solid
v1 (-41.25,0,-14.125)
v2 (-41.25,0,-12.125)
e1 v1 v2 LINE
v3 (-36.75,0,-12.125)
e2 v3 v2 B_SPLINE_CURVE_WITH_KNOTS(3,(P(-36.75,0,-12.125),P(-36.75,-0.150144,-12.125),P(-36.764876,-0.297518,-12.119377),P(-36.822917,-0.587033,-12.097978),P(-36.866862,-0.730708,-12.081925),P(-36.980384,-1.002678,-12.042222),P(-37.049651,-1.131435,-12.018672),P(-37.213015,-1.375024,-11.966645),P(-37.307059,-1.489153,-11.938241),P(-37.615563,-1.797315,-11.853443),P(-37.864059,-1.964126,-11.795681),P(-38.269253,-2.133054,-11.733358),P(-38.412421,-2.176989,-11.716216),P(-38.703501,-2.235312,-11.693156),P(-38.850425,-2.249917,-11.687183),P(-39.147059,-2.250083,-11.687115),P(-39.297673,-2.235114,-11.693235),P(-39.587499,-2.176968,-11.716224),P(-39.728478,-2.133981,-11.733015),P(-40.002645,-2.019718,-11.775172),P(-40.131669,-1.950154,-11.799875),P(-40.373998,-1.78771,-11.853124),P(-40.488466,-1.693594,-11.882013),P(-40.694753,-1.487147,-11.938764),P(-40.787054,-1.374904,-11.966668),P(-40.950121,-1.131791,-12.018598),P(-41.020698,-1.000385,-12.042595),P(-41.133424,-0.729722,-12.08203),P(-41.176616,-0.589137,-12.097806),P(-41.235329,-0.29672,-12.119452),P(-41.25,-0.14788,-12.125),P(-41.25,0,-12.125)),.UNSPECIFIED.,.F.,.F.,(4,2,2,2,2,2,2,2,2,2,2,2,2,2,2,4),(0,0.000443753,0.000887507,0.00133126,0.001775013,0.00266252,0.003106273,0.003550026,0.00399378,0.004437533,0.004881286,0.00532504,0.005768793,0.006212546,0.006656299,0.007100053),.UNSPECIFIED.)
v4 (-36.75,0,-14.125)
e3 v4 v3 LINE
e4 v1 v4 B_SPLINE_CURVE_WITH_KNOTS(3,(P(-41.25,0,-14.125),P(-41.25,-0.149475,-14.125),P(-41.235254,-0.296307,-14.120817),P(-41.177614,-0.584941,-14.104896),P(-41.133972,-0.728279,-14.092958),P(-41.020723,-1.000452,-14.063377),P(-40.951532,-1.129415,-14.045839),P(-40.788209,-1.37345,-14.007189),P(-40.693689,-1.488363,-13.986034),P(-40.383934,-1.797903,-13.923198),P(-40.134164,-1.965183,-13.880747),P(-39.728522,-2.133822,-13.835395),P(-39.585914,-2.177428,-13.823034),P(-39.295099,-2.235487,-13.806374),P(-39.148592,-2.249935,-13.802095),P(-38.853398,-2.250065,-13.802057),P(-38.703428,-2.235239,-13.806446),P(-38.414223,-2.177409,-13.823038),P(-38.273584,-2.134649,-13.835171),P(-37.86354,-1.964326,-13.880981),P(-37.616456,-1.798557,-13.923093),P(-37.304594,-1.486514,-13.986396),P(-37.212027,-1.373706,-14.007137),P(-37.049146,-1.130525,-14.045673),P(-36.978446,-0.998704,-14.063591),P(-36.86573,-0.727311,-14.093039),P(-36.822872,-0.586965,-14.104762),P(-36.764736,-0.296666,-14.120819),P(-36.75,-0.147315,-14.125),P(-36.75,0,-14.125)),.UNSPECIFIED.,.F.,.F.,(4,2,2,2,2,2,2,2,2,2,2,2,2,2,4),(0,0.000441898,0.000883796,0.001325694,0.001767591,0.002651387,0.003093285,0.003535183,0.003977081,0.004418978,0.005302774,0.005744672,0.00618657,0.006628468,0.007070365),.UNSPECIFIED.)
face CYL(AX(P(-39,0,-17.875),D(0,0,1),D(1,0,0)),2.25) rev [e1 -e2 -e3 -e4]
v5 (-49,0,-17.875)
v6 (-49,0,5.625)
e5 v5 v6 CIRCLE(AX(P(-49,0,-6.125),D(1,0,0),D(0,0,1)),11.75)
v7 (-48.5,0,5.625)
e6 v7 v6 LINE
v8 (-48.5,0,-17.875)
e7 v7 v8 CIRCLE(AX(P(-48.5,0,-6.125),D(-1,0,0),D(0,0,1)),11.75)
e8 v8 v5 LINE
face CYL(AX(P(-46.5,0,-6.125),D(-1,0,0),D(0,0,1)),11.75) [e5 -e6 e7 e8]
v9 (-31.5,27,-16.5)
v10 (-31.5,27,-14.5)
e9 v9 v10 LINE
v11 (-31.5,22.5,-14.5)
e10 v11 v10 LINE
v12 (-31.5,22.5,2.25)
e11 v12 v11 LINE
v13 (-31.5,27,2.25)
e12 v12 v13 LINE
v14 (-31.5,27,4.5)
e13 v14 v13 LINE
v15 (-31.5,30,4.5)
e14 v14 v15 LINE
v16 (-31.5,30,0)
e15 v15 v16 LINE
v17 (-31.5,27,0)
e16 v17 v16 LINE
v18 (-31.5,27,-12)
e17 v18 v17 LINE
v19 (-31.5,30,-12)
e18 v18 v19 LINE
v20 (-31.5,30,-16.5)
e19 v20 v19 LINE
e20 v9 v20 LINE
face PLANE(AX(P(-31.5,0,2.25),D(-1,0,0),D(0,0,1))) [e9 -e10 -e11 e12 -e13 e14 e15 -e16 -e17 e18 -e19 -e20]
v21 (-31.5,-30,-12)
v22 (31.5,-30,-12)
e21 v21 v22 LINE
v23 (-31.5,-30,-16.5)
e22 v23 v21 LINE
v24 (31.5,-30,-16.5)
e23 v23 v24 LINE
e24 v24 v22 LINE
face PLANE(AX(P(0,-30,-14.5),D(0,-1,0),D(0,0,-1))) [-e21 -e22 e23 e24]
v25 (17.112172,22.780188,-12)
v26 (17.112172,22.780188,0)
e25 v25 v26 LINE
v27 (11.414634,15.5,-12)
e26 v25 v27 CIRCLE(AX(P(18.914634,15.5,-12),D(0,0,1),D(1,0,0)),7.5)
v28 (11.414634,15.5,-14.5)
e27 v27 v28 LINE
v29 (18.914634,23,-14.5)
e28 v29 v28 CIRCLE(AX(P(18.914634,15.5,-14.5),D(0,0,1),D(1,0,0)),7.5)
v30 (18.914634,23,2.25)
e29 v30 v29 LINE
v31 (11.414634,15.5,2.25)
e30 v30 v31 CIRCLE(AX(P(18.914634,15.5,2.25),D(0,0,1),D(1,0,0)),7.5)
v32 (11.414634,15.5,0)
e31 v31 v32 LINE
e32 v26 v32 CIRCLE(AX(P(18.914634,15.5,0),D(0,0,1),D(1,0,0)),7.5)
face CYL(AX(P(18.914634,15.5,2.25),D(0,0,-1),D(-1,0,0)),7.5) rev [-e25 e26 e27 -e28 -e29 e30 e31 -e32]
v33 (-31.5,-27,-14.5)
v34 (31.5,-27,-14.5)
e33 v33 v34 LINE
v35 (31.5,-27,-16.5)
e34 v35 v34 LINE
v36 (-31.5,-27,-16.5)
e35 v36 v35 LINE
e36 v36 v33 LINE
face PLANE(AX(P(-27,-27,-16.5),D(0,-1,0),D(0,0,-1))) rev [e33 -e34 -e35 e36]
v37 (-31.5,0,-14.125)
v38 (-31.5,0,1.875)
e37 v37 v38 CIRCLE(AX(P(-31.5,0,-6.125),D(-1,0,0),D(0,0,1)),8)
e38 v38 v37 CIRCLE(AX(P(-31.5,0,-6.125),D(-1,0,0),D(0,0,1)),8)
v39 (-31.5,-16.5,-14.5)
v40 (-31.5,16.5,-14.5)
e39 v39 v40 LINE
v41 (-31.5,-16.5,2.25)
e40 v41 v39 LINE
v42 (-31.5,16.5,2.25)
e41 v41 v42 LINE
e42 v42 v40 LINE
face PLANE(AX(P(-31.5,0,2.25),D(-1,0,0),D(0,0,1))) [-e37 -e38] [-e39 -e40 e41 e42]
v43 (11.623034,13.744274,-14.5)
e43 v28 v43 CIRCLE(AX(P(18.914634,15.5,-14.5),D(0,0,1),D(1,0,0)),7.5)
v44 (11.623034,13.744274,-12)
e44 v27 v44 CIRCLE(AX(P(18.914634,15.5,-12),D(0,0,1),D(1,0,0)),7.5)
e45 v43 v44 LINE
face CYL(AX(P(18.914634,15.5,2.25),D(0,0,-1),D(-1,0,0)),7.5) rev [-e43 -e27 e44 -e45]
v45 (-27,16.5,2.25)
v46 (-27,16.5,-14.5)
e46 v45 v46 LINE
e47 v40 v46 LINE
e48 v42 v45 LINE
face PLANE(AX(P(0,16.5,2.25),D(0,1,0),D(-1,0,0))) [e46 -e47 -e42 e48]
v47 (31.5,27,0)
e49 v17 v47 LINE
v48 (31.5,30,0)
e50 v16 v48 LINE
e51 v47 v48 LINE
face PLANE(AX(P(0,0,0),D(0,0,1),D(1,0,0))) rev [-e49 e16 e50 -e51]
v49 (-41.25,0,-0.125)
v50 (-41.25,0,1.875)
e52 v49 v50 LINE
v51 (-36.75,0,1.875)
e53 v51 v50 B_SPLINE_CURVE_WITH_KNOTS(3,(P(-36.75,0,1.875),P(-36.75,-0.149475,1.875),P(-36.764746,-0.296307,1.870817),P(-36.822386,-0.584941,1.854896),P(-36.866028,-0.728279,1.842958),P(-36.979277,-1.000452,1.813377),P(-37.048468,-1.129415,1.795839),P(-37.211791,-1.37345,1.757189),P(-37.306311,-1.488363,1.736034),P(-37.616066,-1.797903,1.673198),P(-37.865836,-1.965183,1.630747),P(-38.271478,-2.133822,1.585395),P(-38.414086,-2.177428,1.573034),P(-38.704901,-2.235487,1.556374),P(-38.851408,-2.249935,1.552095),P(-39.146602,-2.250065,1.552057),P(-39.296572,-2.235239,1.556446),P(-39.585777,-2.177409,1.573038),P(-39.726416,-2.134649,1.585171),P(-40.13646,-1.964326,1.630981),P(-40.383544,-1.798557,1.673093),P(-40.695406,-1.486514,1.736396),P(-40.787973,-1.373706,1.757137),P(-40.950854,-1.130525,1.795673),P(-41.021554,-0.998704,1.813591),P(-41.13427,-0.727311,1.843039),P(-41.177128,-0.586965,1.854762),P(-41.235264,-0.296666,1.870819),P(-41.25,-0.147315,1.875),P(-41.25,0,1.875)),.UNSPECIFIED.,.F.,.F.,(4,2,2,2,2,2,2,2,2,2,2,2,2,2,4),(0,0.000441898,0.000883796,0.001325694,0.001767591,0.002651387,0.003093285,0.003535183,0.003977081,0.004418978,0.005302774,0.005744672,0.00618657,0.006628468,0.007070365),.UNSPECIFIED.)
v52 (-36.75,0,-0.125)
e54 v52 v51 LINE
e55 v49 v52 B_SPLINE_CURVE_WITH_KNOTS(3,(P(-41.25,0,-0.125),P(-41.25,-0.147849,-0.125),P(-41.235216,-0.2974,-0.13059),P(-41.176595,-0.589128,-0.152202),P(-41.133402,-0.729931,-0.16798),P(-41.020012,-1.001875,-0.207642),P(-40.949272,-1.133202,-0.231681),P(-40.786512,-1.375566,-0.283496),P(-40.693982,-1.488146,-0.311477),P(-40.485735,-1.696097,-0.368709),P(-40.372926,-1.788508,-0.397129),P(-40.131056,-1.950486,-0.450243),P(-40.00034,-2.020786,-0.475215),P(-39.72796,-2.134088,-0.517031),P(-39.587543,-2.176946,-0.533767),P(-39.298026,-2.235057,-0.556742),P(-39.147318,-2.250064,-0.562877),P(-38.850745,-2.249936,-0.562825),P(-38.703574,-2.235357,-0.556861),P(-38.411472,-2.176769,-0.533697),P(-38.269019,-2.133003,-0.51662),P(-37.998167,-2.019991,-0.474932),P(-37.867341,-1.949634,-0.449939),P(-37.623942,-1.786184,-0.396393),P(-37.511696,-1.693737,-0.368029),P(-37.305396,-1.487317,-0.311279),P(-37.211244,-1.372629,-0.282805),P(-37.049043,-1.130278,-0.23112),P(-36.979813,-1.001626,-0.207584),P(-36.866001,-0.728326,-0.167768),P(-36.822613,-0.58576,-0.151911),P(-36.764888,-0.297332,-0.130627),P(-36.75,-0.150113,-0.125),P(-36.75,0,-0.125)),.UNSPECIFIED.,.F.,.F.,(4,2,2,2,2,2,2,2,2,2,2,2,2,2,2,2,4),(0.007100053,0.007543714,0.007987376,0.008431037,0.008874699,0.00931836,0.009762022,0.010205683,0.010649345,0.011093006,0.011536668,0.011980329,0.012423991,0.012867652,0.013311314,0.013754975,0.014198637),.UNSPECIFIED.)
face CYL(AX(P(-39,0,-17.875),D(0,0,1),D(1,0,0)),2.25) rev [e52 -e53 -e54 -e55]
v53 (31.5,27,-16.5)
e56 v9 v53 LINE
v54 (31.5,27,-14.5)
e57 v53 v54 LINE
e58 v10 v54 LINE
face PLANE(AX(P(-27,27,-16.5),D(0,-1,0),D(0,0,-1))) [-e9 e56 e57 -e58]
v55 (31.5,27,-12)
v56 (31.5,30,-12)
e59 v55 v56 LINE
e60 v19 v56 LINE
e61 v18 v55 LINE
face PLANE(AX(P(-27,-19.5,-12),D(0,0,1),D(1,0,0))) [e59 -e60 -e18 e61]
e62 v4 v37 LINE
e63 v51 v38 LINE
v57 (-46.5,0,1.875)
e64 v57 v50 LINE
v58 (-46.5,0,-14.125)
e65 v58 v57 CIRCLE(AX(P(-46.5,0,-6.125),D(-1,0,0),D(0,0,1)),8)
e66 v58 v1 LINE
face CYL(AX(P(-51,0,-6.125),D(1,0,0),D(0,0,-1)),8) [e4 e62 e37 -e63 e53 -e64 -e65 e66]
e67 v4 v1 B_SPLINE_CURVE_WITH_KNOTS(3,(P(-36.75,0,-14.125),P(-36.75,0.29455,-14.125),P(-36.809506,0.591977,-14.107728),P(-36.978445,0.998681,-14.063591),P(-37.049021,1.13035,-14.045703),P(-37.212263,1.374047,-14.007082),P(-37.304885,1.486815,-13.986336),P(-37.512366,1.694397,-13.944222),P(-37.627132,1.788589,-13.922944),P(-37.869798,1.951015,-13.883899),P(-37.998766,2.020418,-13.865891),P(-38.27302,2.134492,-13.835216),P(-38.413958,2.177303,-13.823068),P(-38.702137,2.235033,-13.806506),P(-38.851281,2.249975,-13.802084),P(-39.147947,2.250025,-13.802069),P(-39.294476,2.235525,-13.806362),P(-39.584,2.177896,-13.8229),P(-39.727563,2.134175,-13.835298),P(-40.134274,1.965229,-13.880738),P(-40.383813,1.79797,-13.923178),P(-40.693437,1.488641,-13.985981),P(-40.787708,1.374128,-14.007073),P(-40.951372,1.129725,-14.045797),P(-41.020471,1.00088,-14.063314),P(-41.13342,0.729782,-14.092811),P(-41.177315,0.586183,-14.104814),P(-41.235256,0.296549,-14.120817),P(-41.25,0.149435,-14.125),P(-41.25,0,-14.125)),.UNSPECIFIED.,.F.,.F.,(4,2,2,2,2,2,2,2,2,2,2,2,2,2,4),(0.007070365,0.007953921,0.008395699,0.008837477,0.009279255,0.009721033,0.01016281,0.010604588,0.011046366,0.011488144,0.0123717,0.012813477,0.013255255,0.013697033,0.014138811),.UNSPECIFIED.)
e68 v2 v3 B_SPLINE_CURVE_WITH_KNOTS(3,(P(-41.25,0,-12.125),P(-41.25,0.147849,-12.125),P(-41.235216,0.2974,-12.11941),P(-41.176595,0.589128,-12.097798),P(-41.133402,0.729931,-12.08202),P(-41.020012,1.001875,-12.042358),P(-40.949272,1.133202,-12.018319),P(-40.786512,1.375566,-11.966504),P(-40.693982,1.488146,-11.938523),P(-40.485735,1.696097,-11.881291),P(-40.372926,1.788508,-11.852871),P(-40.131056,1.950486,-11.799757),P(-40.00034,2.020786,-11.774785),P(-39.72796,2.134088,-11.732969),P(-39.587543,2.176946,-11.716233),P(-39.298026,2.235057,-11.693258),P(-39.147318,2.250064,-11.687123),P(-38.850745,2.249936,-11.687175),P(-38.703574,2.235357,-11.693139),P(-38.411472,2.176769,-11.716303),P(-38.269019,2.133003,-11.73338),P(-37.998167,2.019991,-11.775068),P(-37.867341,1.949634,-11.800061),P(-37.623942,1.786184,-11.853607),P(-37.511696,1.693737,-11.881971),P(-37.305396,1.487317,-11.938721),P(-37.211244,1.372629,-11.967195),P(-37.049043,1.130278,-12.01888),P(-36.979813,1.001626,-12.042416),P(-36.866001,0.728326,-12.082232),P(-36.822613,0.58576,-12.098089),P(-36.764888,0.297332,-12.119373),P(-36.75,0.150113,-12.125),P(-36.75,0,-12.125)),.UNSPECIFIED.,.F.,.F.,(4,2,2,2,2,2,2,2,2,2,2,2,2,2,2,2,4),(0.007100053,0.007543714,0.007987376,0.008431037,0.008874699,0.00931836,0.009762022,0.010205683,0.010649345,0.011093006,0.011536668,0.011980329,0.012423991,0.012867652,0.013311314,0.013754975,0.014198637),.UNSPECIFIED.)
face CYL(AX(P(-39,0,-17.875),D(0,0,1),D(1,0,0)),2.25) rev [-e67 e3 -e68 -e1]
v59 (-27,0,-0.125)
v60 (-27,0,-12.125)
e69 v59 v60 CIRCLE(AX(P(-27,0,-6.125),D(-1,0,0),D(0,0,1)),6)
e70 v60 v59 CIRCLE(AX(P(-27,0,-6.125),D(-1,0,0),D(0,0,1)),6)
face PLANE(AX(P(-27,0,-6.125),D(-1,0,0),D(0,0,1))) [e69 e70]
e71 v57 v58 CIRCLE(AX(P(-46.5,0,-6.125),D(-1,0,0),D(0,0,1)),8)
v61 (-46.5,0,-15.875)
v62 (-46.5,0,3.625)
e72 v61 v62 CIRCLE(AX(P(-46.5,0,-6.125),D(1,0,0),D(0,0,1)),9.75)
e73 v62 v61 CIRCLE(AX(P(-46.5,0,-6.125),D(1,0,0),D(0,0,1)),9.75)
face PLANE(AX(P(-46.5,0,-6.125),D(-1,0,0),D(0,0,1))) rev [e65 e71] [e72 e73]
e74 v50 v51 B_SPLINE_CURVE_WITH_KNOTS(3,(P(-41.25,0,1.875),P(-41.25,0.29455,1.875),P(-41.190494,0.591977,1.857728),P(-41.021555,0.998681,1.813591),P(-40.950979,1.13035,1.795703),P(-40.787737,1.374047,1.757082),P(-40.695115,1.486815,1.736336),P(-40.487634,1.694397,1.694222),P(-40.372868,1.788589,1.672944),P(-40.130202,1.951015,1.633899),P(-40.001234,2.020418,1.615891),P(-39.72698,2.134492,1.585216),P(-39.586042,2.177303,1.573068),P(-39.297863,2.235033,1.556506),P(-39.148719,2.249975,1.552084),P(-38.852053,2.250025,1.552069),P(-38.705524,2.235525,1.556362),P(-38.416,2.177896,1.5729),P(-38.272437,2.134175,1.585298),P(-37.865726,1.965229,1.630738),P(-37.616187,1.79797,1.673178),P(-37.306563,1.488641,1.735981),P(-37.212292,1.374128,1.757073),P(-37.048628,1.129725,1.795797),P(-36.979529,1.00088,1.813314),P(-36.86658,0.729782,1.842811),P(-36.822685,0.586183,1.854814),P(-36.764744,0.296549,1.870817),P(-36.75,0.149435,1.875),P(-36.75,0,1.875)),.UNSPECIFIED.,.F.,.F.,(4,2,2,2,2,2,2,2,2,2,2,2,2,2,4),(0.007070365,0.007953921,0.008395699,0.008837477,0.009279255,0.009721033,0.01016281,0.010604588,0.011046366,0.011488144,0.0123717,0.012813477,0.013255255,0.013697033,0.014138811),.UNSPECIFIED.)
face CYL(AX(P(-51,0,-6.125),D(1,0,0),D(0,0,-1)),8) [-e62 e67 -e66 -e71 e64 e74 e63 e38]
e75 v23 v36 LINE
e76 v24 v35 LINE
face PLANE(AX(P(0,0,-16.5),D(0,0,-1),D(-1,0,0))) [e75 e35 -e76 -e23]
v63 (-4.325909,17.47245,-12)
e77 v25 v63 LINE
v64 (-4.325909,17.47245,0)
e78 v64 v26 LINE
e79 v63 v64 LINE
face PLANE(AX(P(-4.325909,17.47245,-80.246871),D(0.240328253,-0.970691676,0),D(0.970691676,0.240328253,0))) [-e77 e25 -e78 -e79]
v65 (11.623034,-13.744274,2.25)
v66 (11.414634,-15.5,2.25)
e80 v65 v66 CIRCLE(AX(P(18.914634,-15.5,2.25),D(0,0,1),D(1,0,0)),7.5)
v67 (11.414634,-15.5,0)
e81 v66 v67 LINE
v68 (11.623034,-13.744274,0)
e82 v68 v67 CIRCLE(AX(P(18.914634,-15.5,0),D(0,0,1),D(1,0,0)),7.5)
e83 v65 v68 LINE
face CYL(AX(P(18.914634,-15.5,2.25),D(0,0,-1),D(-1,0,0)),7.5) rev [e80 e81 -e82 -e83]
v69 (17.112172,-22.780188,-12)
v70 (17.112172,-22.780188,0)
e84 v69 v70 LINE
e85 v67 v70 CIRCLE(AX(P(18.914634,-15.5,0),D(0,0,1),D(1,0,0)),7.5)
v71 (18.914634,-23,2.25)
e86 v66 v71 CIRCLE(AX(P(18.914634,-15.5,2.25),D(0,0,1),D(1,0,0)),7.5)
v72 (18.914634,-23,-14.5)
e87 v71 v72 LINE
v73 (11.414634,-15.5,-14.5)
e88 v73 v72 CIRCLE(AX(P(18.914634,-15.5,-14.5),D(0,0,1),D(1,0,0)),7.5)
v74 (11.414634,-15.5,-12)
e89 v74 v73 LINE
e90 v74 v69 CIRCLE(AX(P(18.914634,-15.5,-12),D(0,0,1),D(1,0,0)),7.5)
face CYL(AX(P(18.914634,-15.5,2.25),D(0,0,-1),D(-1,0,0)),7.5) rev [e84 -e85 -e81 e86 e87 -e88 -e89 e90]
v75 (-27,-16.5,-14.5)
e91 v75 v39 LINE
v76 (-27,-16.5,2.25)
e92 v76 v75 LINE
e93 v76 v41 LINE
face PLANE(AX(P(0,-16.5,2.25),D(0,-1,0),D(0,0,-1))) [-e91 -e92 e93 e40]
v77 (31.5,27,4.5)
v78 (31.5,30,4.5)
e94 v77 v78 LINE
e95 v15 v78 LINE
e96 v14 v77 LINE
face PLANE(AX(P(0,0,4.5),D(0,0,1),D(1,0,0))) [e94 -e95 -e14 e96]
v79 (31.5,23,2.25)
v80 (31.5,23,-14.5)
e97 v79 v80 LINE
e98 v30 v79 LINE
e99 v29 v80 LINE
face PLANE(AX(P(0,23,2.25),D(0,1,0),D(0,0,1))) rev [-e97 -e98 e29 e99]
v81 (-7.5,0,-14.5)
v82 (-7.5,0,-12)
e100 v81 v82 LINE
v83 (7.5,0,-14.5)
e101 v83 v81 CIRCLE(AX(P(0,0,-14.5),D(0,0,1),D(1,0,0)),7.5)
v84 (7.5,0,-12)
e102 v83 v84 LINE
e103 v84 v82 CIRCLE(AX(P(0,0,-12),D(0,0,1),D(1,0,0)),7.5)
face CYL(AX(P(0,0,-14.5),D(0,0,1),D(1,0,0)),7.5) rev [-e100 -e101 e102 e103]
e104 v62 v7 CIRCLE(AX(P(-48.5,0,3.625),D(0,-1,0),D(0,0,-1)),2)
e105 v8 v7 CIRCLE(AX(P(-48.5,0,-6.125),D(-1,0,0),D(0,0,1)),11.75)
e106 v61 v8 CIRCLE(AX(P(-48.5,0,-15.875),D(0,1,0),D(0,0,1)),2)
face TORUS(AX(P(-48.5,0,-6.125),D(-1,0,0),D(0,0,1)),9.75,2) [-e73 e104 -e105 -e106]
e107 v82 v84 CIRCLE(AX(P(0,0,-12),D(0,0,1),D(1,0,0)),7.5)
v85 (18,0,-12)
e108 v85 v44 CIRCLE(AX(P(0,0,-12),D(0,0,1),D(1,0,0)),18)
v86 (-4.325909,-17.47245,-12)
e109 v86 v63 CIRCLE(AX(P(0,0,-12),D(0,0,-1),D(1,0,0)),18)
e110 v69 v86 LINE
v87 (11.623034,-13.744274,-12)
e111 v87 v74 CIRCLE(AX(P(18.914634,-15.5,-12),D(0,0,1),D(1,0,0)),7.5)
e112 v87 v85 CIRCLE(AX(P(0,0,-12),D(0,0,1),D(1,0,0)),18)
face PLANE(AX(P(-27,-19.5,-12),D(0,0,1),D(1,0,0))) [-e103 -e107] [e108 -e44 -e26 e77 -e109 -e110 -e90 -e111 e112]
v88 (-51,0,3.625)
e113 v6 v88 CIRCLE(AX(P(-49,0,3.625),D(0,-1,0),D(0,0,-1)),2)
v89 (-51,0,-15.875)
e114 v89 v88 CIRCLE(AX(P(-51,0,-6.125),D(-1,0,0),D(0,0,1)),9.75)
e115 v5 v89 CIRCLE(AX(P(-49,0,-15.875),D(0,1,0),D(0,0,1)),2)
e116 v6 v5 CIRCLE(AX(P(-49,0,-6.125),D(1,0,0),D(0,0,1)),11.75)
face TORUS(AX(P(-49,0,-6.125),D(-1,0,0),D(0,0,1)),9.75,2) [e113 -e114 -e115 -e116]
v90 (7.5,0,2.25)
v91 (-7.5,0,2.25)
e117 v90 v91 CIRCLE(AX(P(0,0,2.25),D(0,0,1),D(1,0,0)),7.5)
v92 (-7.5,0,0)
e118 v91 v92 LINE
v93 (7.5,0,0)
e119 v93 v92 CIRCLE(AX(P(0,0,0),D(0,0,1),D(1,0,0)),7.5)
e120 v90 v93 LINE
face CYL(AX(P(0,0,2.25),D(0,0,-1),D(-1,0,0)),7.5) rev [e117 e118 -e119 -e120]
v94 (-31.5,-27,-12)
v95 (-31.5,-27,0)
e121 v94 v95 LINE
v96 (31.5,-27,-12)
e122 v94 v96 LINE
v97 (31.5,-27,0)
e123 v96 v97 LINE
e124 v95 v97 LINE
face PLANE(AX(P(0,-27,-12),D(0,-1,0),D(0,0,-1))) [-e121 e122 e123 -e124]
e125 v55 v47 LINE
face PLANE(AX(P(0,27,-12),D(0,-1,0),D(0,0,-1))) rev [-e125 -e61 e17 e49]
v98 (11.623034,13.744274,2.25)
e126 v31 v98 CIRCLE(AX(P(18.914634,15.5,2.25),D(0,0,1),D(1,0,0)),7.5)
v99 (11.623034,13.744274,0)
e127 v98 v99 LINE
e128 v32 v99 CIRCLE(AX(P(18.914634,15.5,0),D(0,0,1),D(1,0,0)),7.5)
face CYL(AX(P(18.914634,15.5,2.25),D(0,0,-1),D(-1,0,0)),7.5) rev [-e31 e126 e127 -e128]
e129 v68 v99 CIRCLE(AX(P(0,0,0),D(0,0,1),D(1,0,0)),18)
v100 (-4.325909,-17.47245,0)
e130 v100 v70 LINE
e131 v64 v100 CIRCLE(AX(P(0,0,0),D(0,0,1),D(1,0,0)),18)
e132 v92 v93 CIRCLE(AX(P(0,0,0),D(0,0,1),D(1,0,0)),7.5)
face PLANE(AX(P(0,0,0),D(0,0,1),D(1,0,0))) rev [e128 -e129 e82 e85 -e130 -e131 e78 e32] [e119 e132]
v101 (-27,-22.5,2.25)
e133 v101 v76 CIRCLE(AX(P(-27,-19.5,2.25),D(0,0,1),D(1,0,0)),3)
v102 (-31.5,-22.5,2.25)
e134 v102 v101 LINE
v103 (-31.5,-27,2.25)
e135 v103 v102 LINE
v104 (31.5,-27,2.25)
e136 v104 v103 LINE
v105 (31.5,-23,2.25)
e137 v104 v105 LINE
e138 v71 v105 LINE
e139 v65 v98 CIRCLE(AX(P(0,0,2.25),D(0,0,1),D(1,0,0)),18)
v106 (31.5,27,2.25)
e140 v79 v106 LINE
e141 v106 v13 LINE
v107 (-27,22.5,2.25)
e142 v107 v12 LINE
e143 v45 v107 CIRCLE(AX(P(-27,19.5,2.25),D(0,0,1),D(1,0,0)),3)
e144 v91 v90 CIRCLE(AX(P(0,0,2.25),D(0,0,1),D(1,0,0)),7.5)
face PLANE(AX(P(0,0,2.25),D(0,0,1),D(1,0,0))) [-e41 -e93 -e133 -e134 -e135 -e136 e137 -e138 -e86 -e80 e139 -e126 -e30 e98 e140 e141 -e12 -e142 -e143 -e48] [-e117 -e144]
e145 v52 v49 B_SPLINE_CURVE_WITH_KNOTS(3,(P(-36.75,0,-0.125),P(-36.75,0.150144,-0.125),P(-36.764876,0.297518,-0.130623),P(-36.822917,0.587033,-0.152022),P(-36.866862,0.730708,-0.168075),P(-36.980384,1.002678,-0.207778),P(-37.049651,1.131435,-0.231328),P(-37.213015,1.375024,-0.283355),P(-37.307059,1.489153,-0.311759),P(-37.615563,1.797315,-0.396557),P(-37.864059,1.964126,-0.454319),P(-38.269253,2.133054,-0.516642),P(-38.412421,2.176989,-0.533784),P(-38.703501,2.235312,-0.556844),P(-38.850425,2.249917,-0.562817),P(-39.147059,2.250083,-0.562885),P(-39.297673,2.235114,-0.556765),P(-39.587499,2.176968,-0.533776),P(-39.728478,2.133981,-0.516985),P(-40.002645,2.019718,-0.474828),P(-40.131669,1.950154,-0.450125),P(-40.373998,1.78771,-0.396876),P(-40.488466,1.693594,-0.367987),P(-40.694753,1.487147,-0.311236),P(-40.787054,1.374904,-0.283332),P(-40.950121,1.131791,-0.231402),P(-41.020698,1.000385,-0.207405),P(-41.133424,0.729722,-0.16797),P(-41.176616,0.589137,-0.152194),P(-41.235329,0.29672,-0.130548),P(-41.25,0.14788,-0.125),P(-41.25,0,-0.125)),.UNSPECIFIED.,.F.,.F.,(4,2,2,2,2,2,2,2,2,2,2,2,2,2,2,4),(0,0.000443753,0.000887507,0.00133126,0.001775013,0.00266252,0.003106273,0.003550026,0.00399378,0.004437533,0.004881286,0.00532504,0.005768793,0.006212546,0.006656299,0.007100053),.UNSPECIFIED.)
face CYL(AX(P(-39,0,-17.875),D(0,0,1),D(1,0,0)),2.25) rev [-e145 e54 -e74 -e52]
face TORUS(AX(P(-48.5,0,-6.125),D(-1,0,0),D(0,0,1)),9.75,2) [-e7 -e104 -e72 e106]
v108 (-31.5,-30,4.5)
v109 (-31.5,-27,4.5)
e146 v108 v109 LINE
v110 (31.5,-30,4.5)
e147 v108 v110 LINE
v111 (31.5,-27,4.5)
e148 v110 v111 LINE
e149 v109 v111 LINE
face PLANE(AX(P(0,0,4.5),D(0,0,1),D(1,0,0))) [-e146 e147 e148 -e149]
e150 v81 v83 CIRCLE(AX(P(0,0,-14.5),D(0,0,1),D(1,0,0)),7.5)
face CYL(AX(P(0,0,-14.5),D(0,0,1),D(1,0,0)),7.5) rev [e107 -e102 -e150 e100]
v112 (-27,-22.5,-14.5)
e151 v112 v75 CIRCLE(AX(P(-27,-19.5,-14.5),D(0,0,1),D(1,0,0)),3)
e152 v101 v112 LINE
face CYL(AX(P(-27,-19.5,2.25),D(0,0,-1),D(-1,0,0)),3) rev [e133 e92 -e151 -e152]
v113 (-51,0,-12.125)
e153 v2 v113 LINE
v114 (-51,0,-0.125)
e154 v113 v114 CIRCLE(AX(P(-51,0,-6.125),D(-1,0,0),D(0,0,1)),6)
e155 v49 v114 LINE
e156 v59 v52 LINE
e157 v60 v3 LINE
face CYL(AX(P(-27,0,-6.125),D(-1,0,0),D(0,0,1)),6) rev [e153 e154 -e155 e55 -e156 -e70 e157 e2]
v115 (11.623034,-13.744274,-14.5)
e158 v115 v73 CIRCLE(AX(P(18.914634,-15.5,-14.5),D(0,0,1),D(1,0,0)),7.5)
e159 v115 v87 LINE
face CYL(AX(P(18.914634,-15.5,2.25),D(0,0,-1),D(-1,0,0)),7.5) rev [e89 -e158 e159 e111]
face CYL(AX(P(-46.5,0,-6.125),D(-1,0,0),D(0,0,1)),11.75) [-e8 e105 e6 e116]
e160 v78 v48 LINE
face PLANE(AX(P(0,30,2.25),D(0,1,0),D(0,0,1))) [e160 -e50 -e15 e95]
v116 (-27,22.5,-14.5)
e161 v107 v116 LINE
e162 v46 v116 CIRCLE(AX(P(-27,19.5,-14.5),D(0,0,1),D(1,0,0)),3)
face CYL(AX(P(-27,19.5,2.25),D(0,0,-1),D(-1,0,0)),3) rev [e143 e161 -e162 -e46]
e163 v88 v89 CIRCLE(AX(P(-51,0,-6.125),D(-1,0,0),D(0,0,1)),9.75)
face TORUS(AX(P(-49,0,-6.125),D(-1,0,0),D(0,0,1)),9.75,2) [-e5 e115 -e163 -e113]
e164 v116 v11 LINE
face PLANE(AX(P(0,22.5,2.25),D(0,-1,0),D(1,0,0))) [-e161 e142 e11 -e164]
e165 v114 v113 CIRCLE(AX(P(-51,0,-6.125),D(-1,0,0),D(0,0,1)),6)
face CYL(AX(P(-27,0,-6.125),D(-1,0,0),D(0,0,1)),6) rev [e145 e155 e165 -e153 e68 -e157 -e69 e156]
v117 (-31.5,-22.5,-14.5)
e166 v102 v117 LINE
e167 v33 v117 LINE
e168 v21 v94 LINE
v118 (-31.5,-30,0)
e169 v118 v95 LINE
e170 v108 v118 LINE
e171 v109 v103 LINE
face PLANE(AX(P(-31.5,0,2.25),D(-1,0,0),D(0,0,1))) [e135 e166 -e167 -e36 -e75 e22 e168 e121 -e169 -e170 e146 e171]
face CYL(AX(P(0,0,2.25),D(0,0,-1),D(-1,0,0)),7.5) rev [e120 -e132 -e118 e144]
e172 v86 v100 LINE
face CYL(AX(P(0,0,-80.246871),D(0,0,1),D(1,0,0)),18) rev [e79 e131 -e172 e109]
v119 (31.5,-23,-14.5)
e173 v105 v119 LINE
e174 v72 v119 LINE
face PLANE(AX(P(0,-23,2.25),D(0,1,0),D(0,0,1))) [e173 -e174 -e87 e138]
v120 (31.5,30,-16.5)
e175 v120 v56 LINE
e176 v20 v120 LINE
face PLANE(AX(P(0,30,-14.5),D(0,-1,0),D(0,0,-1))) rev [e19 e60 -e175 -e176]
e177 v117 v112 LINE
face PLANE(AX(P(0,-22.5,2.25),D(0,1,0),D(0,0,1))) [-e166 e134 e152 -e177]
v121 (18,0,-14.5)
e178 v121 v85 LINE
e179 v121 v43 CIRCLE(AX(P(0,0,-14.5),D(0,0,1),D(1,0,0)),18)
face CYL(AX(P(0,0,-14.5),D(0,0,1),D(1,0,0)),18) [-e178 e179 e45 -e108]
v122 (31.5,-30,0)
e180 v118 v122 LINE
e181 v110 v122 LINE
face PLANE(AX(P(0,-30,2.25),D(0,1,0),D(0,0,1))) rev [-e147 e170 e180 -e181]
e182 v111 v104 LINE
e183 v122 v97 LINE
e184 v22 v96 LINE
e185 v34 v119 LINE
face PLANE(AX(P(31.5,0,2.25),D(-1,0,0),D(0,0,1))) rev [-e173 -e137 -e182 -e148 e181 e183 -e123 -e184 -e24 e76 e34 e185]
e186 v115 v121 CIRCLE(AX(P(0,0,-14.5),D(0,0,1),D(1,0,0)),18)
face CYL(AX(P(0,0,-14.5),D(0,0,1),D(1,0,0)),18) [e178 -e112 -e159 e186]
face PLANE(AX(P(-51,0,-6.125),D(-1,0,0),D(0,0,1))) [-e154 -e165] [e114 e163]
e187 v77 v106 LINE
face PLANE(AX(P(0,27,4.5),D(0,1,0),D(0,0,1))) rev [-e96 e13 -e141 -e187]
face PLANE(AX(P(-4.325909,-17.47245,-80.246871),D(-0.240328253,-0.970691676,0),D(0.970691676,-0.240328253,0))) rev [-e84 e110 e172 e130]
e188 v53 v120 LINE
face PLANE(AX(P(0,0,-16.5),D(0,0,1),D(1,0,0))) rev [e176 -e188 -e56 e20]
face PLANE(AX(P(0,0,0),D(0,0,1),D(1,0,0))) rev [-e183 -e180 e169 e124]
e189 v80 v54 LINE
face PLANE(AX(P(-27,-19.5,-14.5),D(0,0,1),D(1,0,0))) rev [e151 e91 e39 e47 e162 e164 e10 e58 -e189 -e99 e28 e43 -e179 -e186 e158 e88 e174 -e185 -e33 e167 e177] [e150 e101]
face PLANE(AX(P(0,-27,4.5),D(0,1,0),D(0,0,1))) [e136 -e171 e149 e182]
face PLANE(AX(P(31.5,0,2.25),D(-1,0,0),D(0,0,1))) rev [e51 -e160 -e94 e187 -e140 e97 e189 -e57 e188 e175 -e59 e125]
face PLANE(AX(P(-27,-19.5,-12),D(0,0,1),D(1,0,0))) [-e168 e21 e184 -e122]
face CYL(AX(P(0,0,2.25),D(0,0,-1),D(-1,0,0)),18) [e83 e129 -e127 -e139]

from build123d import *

# Parameters (mm, degrees)
I_SECTION_PROFILE_SKETCH_W   = 63
I_SECTION_PROFILE_SKETCH_H   = 3
I_SECTION_PROFILE_SKETCH_R   = 18
I_SECTION_PROFILE_SKETCH_R_2 = 7.5
BASE_PLATE_2_25_DEPTH        = 2.25
SKETCH1_11_W                 = 63
SKETCH1_11_H                 = 3
SECTION_STEP_4_5_DEPTH       = 4.5
SECTION_STEP_12_DEPTH        = 12
SECTION_START                = -14.5
SKETCH1_14_W                 = 63
SKETCH1_14_H                 = 3
SKETCH1_14_R                 = 18
SKETCH1_14_R_2               = 7.5
SECTION_STEP_2_5_DEPTH       = 2.5
SECTION_START_2              = -12
SECTION_STEP_TO_FACE_DEPTH   = 12
SKETCH1_16_W                 = 63
SKETCH1_16_H                 = 3
SECTION_STEP_2_DEPTH         = 2
HUB_SKETCH_16_R              = 8
HUB_16_DEPTH                 = 19.5
FLANGE_SKETCH_23_5_R         = 11.75
FLANGE_23_5_DEPTH            = 4.5
BORE_SKETCH_12_R             = 6
BORE_12_DEPTH                = 24
CROSS_HOLE_4_5_DEPTH         = 62.810319729
CROSS_HOLE_4_5_DEPTH_BACK    = 62.810319729
CROSS_HOLE_SKETCH_4_5_R      = 2.25
FLANGE_FILLET_R2_R           = 2


with BuildPart() as part:
    # I-Section Profile Sketch → Base Plate 2.25 (new body)
    # profile 1 of 8: a face of its own
    with BuildSketch(Plane.XY):
        with Locations((0, 28.5)):
            Rectangle(I_SECTION_PROFILE_SKETCH_W, I_SECTION_PROFILE_SKETCH_H)
    # profile 2 of 8: a face of its own
    with BuildSketch(Plane.XY):
        Polygon((-31.5, 27), (-31.5, 23), (18.914634146, 23), (31.5, 23), (31.5, 27), align=None)
    # profile 3 of 8: a face of its own
    with BuildSketch(Plane.XY):
        with BuildLine():
            ThreePointArc((11.623034417, 13.744274115), (12.504687014, 19.39391548), (17.112172247, 22.780187573))
            Line((17.112172247, 22.780187573), (-4.325908558, 17.472450176))
            ThreePointArc((-4.325908558, 17.472450176), (4.097174104, 17.527497379), (11.623034417, 13.744274115))
        make_face()
    # profile 4 of 8: a face of its own
    with BuildSketch(Plane.XY):
        with BuildLine():
            Line((-31.5, 22.5), (-27, 22.5))
            ThreePointArc((-27, 22.5), (-24, 19.5), (-27, 16.5))
            Line((-27, 16.5), (-31.5, 16.5))
            Line((-31.5, 16.5), (-31.5, -16.5))
            Line((-31.5, -16.5), (-27, -16.5))
            ThreePointArc((-27, -16.5), (-24, -19.5), (-27, -22.5))
            Line((-27, -22.5), (-31.5, -22.5))
            Line((-31.5, -22.5), (-31.5, -23))
            Line((-31.5, -23), (18.914634146, -23))
            ThreePointArc((18.914634146, -23), (18.006726332, -22.944844082), (17.112172247, -22.780187573))
            Line((17.112172247, -22.780187573), (-4.325908558, -17.472450176))
            ThreePointArc((-4.325908558, -17.472450176), (-18, 0), (-4.325908558, 17.472450176))
            Line((-4.325908558, 17.472450176), (17.112172247, 22.780187573))
            ThreePointArc((17.112172247, 22.780187573), (18.006726332, 22.944844082), (18.914634146, 23))
            Line((18.914634146, 23), (-31.5, 23))
            Line((-31.5, 23), (-31.5, 22.5))
        make_face()
    # profile 5 of 8: a face of its own
    with BuildSketch(Plane.XY):
        Circle(I_SECTION_PROFILE_SKETCH_R)
        Circle(I_SECTION_PROFILE_SKETCH_R_2, mode=Mode.SUBTRACT)
    # profile 6 of 8: a face of its own
    with BuildSketch(Plane.XY):
        Polygon((31.5, -27), (31.5, -23), (18.914634146, -23), (-31.5, -23), (-31.5, -27), align=None)
    # profile 7 of 8: a face of its own
    with BuildSketch(Plane.XY):
        with Locations((0, -28.5)):
            Rectangle(I_SECTION_PROFILE_SKETCH_W, I_SECTION_PROFILE_SKETCH_H)
    # profile 8 of 8: a face of its own
    with BuildSketch(Plane.XY):
        with BuildLine():
            ThreePointArc((11.623034417, -13.744274115), (4.097174104, -17.527497379), (-4.325908558, -17.472450176))
            Line((-4.325908558, -17.472450176), (17.112172247, -22.780187573))
            ThreePointArc((17.112172247, -22.780187573), (12.504687014, -19.39391548), (11.623034417, -13.744274115))
        make_face()
    extrude(amount=BASE_PLATE_2_25_DEPTH)

    # Sketch1_11 → Section Step 4.5 (add)
    with BuildSketch(Plane.XY):
        with Locations((0, 28.5)):
            Rectangle(SKETCH1_11_W, SKETCH1_11_H)
        with Locations((0, -28.5)):
            Rectangle(SKETCH1_11_W, SKETCH1_11_H)
    extrude(amount=SECTION_STEP_4_5_DEPTH)

    # Sketch1_13 → Section Step 12 (add)
    with BuildSketch(Plane.XY):
        Polygon((-31.5, 27), (-31.5, 23), (18.914634146, 23), (31.5, 23), (31.5, 27), align=None)
        Polygon((31.5, -27), (31.5, -23), (18.914634146, -23), (-31.5, -23), (-31.5, -27), align=None)
    extrude(amount=-SECTION_STEP_12_DEPTH)

    # Sketch1_14 → Section Step 2.5 (add)
    # profile 1 of 8: a face of its own
    with BuildSketch(Plane.XY.offset(SECTION_START)):
        with Locations((0, 28.5)):
            Rectangle(SKETCH1_14_W, SKETCH1_14_H)
    # profile 2 of 8: a face of its own
    with BuildSketch(Plane.XY.offset(SECTION_START)):
        Polygon((-31.5, 27), (-31.5, 23), (18.914634146, 23), (31.5, 23), (31.5, 27), align=None)
    # profile 3 of 8: a face of its own
    with BuildSketch(Plane.XY.offset(SECTION_START)):
        with BuildLine():
            Line((-31.5, 22.5), (-27, 22.5))
            ThreePointArc((-27, 22.5), (-24, 19.5), (-27, 16.5))
            Line((-27, 16.5), (-31.5, 16.5))
            Line((-31.5, 16.5), (-31.5, -16.5))
            Line((-31.5, -16.5), (-27, -16.5))
            ThreePointArc((-27, -16.5), (-24, -19.5), (-27, -22.5))
            Line((-27, -22.5), (-31.5, -22.5))
            Line((-31.5, -22.5), (-31.5, -23))
            Line((-31.5, -23), (18.914634146, -23))
            ThreePointArc((18.914634146, -23), (18.006726332, -22.944844082), (17.112172247, -22.780187573))
            Line((17.112172247, -22.780187573), (-4.325908558, -17.472450176))
            ThreePointArc((-4.325908558, -17.472450176), (-18, 0), (-4.325908558, 17.472450176))
            Line((-4.325908558, 17.472450176), (17.112172247, 22.780187573))
            ThreePointArc((17.112172247, 22.780187573), (18.006726332, 22.944844082), (18.914634146, 23))
            Line((18.914634146, 23), (-31.5, 23))
            Line((-31.5, 23), (-31.5, 22.5))
        make_face()
    # profile 4 of 8: a face of its own
    with BuildSketch(Plane.XY.offset(SECTION_START)):
        Circle(SKETCH1_14_R)
        Circle(SKETCH1_14_R_2, mode=Mode.SUBTRACT)
    # profile 5 of 8: a face of its own
    with BuildSketch(Plane.XY.offset(SECTION_START)):
        with BuildLine():
            ThreePointArc((11.623034417, 13.744274115), (12.504687014, 19.39391548), (17.112172247, 22.780187573))
            Line((17.112172247, 22.780187573), (-4.325908558, 17.472450176))
            ThreePointArc((-4.325908558, 17.472450176), (4.097174104, 17.527497379), (11.623034417, 13.744274115))
        make_face()
    # profile 6 of 8: a face of its own
    with BuildSketch(Plane.XY.offset(SECTION_START)):
        with BuildLine():
            ThreePointArc((11.623034417, -13.744274115), (4.097174104, -17.527497379), (-4.325908558, -17.472450176))
            Line((-4.325908558, -17.472450176), (17.112172247, -22.780187573))
            ThreePointArc((17.112172247, -22.780187573), (12.504687014, -19.39391548), (11.623034417, -13.744274115))
        make_face()
    # profile 7 of 8: a face of its own
    with BuildSketch(Plane.XY.offset(SECTION_START)):
        Polygon((31.5, -27), (31.5, -23), (18.914634146, -23), (-31.5, -23), (-31.5, -27), align=None)
    # profile 8 of 8: a face of its own
    with BuildSketch(Plane.XY.offset(SECTION_START)):
        with Locations((0, -28.5)):
            Rectangle(SKETCH1_14_W, SKETCH1_14_H)
    extrude(amount=SECTION_STEP_2_5_DEPTH)

    # Sketch1_15 → Section Step To Face (add)
    with BuildSketch(Plane.XY.offset(SECTION_START_2)):
        with BuildLine():
            Line((-31.5, 22.5), (-27, 22.5))
            ThreePointArc((-27, 22.5), (-24, 19.5), (-27, 16.5))
            Line((-27, 16.5), (-31.5, 16.5))
            Line((-31.5, 16.5), (-31.5, -16.5))
            Line((-31.5, -16.5), (-27, -16.5))
            ThreePointArc((-27, -16.5), (-24, -19.5), (-27, -22.5))
            Line((-27, -22.5), (-31.5, -22.5))
            Line((-31.5, -22.5), (-31.5, -23))
            Line((-31.5, -23), (18.914634146, -23))
            ThreePointArc((18.914634146, -23), (18.006726332, -22.944844082), (17.112172247, -22.780187573))
            Line((17.112172247, -22.780187573), (-4.325908558, -17.472450176))
            ThreePointArc((-4.325908558, -17.472450176), (-18, 0), (-4.325908558, 17.472450176))
            Line((-4.325908558, 17.472450176), (17.112172247, 22.780187573))
            ThreePointArc((17.112172247, 22.780187573), (18.006726332, 22.944844082), (18.914634146, 23))
            Line((18.914634146, 23), (-31.5, 23))
            Line((-31.5, 23), (-31.5, 22.5))
        make_face()
    extrude(amount=SECTION_STEP_TO_FACE_DEPTH)

    # Sketch1_16 → Section Step 2 (add)
    with BuildSketch(Plane.XY.offset(SECTION_START)):
        with Locations((0, 28.5)):
            Rectangle(SKETCH1_16_W, SKETCH1_16_H)
        with Locations((0, -28.5)):
            Rectangle(SKETCH1_16_W, SKETCH1_16_H)
    extrude(amount=-SECTION_STEP_2_DEPTH)

    # Hub Sketch _16 → Hub _16 (add)
    with BuildSketch(Plane.ZY.offset(31.5)):
        with Locations((-6.125, 0)):
            Circle(HUB_SKETCH_16_R)
    extrude(amount=HUB_16_DEPTH)

    # Flange Sketch _23.5 → Flange _23.5 (add)
    with BuildSketch(Plane.ZY.offset(51)):
        with Locations((-6.125, 0)):
            Circle(FLANGE_SKETCH_23_5_R)
    extrude(amount=-FLANGE_23_5_DEPTH)

    # Bore Sketch _12 → Bore _12 (cut)
    with BuildSketch(Plane.ZY.offset(51)):
        with Locations((-6.125, 0)):
            Circle(BORE_SKETCH_12_R)
    extrude(amount=-BORE_12_DEPTH, mode=Mode.SUBTRACT)

    # Cross Hole Sketch _4.5 → Cross Hole _4.5 (cut, two sides: drawn at the far end of the back side and taken through both)
    with BuildSketch(Plane.XY.offset(-CROSS_HOLE_4_5_DEPTH_BACK)):
        with Locations((-39, 0)):
            Circle(CROSS_HOLE_SKETCH_4_5_R)
    extrude(amount=CROSS_HOLE_4_5_DEPTH + CROSS_HOLE_4_5_DEPTH_BACK, mode=Mode.SUBTRACT)

    # Flange Fillet R2
    flange_fillet_r2_edges = [part.edges().sort_by_distance(p)[0] for p in [
        (-46.5, 0, -17.875),
        (-51, 0, -17.875),
    ]]
    fillet(flange_fillet_r2_edges, radius=FLANGE_FILLET_R2_R)


solid = part.part
